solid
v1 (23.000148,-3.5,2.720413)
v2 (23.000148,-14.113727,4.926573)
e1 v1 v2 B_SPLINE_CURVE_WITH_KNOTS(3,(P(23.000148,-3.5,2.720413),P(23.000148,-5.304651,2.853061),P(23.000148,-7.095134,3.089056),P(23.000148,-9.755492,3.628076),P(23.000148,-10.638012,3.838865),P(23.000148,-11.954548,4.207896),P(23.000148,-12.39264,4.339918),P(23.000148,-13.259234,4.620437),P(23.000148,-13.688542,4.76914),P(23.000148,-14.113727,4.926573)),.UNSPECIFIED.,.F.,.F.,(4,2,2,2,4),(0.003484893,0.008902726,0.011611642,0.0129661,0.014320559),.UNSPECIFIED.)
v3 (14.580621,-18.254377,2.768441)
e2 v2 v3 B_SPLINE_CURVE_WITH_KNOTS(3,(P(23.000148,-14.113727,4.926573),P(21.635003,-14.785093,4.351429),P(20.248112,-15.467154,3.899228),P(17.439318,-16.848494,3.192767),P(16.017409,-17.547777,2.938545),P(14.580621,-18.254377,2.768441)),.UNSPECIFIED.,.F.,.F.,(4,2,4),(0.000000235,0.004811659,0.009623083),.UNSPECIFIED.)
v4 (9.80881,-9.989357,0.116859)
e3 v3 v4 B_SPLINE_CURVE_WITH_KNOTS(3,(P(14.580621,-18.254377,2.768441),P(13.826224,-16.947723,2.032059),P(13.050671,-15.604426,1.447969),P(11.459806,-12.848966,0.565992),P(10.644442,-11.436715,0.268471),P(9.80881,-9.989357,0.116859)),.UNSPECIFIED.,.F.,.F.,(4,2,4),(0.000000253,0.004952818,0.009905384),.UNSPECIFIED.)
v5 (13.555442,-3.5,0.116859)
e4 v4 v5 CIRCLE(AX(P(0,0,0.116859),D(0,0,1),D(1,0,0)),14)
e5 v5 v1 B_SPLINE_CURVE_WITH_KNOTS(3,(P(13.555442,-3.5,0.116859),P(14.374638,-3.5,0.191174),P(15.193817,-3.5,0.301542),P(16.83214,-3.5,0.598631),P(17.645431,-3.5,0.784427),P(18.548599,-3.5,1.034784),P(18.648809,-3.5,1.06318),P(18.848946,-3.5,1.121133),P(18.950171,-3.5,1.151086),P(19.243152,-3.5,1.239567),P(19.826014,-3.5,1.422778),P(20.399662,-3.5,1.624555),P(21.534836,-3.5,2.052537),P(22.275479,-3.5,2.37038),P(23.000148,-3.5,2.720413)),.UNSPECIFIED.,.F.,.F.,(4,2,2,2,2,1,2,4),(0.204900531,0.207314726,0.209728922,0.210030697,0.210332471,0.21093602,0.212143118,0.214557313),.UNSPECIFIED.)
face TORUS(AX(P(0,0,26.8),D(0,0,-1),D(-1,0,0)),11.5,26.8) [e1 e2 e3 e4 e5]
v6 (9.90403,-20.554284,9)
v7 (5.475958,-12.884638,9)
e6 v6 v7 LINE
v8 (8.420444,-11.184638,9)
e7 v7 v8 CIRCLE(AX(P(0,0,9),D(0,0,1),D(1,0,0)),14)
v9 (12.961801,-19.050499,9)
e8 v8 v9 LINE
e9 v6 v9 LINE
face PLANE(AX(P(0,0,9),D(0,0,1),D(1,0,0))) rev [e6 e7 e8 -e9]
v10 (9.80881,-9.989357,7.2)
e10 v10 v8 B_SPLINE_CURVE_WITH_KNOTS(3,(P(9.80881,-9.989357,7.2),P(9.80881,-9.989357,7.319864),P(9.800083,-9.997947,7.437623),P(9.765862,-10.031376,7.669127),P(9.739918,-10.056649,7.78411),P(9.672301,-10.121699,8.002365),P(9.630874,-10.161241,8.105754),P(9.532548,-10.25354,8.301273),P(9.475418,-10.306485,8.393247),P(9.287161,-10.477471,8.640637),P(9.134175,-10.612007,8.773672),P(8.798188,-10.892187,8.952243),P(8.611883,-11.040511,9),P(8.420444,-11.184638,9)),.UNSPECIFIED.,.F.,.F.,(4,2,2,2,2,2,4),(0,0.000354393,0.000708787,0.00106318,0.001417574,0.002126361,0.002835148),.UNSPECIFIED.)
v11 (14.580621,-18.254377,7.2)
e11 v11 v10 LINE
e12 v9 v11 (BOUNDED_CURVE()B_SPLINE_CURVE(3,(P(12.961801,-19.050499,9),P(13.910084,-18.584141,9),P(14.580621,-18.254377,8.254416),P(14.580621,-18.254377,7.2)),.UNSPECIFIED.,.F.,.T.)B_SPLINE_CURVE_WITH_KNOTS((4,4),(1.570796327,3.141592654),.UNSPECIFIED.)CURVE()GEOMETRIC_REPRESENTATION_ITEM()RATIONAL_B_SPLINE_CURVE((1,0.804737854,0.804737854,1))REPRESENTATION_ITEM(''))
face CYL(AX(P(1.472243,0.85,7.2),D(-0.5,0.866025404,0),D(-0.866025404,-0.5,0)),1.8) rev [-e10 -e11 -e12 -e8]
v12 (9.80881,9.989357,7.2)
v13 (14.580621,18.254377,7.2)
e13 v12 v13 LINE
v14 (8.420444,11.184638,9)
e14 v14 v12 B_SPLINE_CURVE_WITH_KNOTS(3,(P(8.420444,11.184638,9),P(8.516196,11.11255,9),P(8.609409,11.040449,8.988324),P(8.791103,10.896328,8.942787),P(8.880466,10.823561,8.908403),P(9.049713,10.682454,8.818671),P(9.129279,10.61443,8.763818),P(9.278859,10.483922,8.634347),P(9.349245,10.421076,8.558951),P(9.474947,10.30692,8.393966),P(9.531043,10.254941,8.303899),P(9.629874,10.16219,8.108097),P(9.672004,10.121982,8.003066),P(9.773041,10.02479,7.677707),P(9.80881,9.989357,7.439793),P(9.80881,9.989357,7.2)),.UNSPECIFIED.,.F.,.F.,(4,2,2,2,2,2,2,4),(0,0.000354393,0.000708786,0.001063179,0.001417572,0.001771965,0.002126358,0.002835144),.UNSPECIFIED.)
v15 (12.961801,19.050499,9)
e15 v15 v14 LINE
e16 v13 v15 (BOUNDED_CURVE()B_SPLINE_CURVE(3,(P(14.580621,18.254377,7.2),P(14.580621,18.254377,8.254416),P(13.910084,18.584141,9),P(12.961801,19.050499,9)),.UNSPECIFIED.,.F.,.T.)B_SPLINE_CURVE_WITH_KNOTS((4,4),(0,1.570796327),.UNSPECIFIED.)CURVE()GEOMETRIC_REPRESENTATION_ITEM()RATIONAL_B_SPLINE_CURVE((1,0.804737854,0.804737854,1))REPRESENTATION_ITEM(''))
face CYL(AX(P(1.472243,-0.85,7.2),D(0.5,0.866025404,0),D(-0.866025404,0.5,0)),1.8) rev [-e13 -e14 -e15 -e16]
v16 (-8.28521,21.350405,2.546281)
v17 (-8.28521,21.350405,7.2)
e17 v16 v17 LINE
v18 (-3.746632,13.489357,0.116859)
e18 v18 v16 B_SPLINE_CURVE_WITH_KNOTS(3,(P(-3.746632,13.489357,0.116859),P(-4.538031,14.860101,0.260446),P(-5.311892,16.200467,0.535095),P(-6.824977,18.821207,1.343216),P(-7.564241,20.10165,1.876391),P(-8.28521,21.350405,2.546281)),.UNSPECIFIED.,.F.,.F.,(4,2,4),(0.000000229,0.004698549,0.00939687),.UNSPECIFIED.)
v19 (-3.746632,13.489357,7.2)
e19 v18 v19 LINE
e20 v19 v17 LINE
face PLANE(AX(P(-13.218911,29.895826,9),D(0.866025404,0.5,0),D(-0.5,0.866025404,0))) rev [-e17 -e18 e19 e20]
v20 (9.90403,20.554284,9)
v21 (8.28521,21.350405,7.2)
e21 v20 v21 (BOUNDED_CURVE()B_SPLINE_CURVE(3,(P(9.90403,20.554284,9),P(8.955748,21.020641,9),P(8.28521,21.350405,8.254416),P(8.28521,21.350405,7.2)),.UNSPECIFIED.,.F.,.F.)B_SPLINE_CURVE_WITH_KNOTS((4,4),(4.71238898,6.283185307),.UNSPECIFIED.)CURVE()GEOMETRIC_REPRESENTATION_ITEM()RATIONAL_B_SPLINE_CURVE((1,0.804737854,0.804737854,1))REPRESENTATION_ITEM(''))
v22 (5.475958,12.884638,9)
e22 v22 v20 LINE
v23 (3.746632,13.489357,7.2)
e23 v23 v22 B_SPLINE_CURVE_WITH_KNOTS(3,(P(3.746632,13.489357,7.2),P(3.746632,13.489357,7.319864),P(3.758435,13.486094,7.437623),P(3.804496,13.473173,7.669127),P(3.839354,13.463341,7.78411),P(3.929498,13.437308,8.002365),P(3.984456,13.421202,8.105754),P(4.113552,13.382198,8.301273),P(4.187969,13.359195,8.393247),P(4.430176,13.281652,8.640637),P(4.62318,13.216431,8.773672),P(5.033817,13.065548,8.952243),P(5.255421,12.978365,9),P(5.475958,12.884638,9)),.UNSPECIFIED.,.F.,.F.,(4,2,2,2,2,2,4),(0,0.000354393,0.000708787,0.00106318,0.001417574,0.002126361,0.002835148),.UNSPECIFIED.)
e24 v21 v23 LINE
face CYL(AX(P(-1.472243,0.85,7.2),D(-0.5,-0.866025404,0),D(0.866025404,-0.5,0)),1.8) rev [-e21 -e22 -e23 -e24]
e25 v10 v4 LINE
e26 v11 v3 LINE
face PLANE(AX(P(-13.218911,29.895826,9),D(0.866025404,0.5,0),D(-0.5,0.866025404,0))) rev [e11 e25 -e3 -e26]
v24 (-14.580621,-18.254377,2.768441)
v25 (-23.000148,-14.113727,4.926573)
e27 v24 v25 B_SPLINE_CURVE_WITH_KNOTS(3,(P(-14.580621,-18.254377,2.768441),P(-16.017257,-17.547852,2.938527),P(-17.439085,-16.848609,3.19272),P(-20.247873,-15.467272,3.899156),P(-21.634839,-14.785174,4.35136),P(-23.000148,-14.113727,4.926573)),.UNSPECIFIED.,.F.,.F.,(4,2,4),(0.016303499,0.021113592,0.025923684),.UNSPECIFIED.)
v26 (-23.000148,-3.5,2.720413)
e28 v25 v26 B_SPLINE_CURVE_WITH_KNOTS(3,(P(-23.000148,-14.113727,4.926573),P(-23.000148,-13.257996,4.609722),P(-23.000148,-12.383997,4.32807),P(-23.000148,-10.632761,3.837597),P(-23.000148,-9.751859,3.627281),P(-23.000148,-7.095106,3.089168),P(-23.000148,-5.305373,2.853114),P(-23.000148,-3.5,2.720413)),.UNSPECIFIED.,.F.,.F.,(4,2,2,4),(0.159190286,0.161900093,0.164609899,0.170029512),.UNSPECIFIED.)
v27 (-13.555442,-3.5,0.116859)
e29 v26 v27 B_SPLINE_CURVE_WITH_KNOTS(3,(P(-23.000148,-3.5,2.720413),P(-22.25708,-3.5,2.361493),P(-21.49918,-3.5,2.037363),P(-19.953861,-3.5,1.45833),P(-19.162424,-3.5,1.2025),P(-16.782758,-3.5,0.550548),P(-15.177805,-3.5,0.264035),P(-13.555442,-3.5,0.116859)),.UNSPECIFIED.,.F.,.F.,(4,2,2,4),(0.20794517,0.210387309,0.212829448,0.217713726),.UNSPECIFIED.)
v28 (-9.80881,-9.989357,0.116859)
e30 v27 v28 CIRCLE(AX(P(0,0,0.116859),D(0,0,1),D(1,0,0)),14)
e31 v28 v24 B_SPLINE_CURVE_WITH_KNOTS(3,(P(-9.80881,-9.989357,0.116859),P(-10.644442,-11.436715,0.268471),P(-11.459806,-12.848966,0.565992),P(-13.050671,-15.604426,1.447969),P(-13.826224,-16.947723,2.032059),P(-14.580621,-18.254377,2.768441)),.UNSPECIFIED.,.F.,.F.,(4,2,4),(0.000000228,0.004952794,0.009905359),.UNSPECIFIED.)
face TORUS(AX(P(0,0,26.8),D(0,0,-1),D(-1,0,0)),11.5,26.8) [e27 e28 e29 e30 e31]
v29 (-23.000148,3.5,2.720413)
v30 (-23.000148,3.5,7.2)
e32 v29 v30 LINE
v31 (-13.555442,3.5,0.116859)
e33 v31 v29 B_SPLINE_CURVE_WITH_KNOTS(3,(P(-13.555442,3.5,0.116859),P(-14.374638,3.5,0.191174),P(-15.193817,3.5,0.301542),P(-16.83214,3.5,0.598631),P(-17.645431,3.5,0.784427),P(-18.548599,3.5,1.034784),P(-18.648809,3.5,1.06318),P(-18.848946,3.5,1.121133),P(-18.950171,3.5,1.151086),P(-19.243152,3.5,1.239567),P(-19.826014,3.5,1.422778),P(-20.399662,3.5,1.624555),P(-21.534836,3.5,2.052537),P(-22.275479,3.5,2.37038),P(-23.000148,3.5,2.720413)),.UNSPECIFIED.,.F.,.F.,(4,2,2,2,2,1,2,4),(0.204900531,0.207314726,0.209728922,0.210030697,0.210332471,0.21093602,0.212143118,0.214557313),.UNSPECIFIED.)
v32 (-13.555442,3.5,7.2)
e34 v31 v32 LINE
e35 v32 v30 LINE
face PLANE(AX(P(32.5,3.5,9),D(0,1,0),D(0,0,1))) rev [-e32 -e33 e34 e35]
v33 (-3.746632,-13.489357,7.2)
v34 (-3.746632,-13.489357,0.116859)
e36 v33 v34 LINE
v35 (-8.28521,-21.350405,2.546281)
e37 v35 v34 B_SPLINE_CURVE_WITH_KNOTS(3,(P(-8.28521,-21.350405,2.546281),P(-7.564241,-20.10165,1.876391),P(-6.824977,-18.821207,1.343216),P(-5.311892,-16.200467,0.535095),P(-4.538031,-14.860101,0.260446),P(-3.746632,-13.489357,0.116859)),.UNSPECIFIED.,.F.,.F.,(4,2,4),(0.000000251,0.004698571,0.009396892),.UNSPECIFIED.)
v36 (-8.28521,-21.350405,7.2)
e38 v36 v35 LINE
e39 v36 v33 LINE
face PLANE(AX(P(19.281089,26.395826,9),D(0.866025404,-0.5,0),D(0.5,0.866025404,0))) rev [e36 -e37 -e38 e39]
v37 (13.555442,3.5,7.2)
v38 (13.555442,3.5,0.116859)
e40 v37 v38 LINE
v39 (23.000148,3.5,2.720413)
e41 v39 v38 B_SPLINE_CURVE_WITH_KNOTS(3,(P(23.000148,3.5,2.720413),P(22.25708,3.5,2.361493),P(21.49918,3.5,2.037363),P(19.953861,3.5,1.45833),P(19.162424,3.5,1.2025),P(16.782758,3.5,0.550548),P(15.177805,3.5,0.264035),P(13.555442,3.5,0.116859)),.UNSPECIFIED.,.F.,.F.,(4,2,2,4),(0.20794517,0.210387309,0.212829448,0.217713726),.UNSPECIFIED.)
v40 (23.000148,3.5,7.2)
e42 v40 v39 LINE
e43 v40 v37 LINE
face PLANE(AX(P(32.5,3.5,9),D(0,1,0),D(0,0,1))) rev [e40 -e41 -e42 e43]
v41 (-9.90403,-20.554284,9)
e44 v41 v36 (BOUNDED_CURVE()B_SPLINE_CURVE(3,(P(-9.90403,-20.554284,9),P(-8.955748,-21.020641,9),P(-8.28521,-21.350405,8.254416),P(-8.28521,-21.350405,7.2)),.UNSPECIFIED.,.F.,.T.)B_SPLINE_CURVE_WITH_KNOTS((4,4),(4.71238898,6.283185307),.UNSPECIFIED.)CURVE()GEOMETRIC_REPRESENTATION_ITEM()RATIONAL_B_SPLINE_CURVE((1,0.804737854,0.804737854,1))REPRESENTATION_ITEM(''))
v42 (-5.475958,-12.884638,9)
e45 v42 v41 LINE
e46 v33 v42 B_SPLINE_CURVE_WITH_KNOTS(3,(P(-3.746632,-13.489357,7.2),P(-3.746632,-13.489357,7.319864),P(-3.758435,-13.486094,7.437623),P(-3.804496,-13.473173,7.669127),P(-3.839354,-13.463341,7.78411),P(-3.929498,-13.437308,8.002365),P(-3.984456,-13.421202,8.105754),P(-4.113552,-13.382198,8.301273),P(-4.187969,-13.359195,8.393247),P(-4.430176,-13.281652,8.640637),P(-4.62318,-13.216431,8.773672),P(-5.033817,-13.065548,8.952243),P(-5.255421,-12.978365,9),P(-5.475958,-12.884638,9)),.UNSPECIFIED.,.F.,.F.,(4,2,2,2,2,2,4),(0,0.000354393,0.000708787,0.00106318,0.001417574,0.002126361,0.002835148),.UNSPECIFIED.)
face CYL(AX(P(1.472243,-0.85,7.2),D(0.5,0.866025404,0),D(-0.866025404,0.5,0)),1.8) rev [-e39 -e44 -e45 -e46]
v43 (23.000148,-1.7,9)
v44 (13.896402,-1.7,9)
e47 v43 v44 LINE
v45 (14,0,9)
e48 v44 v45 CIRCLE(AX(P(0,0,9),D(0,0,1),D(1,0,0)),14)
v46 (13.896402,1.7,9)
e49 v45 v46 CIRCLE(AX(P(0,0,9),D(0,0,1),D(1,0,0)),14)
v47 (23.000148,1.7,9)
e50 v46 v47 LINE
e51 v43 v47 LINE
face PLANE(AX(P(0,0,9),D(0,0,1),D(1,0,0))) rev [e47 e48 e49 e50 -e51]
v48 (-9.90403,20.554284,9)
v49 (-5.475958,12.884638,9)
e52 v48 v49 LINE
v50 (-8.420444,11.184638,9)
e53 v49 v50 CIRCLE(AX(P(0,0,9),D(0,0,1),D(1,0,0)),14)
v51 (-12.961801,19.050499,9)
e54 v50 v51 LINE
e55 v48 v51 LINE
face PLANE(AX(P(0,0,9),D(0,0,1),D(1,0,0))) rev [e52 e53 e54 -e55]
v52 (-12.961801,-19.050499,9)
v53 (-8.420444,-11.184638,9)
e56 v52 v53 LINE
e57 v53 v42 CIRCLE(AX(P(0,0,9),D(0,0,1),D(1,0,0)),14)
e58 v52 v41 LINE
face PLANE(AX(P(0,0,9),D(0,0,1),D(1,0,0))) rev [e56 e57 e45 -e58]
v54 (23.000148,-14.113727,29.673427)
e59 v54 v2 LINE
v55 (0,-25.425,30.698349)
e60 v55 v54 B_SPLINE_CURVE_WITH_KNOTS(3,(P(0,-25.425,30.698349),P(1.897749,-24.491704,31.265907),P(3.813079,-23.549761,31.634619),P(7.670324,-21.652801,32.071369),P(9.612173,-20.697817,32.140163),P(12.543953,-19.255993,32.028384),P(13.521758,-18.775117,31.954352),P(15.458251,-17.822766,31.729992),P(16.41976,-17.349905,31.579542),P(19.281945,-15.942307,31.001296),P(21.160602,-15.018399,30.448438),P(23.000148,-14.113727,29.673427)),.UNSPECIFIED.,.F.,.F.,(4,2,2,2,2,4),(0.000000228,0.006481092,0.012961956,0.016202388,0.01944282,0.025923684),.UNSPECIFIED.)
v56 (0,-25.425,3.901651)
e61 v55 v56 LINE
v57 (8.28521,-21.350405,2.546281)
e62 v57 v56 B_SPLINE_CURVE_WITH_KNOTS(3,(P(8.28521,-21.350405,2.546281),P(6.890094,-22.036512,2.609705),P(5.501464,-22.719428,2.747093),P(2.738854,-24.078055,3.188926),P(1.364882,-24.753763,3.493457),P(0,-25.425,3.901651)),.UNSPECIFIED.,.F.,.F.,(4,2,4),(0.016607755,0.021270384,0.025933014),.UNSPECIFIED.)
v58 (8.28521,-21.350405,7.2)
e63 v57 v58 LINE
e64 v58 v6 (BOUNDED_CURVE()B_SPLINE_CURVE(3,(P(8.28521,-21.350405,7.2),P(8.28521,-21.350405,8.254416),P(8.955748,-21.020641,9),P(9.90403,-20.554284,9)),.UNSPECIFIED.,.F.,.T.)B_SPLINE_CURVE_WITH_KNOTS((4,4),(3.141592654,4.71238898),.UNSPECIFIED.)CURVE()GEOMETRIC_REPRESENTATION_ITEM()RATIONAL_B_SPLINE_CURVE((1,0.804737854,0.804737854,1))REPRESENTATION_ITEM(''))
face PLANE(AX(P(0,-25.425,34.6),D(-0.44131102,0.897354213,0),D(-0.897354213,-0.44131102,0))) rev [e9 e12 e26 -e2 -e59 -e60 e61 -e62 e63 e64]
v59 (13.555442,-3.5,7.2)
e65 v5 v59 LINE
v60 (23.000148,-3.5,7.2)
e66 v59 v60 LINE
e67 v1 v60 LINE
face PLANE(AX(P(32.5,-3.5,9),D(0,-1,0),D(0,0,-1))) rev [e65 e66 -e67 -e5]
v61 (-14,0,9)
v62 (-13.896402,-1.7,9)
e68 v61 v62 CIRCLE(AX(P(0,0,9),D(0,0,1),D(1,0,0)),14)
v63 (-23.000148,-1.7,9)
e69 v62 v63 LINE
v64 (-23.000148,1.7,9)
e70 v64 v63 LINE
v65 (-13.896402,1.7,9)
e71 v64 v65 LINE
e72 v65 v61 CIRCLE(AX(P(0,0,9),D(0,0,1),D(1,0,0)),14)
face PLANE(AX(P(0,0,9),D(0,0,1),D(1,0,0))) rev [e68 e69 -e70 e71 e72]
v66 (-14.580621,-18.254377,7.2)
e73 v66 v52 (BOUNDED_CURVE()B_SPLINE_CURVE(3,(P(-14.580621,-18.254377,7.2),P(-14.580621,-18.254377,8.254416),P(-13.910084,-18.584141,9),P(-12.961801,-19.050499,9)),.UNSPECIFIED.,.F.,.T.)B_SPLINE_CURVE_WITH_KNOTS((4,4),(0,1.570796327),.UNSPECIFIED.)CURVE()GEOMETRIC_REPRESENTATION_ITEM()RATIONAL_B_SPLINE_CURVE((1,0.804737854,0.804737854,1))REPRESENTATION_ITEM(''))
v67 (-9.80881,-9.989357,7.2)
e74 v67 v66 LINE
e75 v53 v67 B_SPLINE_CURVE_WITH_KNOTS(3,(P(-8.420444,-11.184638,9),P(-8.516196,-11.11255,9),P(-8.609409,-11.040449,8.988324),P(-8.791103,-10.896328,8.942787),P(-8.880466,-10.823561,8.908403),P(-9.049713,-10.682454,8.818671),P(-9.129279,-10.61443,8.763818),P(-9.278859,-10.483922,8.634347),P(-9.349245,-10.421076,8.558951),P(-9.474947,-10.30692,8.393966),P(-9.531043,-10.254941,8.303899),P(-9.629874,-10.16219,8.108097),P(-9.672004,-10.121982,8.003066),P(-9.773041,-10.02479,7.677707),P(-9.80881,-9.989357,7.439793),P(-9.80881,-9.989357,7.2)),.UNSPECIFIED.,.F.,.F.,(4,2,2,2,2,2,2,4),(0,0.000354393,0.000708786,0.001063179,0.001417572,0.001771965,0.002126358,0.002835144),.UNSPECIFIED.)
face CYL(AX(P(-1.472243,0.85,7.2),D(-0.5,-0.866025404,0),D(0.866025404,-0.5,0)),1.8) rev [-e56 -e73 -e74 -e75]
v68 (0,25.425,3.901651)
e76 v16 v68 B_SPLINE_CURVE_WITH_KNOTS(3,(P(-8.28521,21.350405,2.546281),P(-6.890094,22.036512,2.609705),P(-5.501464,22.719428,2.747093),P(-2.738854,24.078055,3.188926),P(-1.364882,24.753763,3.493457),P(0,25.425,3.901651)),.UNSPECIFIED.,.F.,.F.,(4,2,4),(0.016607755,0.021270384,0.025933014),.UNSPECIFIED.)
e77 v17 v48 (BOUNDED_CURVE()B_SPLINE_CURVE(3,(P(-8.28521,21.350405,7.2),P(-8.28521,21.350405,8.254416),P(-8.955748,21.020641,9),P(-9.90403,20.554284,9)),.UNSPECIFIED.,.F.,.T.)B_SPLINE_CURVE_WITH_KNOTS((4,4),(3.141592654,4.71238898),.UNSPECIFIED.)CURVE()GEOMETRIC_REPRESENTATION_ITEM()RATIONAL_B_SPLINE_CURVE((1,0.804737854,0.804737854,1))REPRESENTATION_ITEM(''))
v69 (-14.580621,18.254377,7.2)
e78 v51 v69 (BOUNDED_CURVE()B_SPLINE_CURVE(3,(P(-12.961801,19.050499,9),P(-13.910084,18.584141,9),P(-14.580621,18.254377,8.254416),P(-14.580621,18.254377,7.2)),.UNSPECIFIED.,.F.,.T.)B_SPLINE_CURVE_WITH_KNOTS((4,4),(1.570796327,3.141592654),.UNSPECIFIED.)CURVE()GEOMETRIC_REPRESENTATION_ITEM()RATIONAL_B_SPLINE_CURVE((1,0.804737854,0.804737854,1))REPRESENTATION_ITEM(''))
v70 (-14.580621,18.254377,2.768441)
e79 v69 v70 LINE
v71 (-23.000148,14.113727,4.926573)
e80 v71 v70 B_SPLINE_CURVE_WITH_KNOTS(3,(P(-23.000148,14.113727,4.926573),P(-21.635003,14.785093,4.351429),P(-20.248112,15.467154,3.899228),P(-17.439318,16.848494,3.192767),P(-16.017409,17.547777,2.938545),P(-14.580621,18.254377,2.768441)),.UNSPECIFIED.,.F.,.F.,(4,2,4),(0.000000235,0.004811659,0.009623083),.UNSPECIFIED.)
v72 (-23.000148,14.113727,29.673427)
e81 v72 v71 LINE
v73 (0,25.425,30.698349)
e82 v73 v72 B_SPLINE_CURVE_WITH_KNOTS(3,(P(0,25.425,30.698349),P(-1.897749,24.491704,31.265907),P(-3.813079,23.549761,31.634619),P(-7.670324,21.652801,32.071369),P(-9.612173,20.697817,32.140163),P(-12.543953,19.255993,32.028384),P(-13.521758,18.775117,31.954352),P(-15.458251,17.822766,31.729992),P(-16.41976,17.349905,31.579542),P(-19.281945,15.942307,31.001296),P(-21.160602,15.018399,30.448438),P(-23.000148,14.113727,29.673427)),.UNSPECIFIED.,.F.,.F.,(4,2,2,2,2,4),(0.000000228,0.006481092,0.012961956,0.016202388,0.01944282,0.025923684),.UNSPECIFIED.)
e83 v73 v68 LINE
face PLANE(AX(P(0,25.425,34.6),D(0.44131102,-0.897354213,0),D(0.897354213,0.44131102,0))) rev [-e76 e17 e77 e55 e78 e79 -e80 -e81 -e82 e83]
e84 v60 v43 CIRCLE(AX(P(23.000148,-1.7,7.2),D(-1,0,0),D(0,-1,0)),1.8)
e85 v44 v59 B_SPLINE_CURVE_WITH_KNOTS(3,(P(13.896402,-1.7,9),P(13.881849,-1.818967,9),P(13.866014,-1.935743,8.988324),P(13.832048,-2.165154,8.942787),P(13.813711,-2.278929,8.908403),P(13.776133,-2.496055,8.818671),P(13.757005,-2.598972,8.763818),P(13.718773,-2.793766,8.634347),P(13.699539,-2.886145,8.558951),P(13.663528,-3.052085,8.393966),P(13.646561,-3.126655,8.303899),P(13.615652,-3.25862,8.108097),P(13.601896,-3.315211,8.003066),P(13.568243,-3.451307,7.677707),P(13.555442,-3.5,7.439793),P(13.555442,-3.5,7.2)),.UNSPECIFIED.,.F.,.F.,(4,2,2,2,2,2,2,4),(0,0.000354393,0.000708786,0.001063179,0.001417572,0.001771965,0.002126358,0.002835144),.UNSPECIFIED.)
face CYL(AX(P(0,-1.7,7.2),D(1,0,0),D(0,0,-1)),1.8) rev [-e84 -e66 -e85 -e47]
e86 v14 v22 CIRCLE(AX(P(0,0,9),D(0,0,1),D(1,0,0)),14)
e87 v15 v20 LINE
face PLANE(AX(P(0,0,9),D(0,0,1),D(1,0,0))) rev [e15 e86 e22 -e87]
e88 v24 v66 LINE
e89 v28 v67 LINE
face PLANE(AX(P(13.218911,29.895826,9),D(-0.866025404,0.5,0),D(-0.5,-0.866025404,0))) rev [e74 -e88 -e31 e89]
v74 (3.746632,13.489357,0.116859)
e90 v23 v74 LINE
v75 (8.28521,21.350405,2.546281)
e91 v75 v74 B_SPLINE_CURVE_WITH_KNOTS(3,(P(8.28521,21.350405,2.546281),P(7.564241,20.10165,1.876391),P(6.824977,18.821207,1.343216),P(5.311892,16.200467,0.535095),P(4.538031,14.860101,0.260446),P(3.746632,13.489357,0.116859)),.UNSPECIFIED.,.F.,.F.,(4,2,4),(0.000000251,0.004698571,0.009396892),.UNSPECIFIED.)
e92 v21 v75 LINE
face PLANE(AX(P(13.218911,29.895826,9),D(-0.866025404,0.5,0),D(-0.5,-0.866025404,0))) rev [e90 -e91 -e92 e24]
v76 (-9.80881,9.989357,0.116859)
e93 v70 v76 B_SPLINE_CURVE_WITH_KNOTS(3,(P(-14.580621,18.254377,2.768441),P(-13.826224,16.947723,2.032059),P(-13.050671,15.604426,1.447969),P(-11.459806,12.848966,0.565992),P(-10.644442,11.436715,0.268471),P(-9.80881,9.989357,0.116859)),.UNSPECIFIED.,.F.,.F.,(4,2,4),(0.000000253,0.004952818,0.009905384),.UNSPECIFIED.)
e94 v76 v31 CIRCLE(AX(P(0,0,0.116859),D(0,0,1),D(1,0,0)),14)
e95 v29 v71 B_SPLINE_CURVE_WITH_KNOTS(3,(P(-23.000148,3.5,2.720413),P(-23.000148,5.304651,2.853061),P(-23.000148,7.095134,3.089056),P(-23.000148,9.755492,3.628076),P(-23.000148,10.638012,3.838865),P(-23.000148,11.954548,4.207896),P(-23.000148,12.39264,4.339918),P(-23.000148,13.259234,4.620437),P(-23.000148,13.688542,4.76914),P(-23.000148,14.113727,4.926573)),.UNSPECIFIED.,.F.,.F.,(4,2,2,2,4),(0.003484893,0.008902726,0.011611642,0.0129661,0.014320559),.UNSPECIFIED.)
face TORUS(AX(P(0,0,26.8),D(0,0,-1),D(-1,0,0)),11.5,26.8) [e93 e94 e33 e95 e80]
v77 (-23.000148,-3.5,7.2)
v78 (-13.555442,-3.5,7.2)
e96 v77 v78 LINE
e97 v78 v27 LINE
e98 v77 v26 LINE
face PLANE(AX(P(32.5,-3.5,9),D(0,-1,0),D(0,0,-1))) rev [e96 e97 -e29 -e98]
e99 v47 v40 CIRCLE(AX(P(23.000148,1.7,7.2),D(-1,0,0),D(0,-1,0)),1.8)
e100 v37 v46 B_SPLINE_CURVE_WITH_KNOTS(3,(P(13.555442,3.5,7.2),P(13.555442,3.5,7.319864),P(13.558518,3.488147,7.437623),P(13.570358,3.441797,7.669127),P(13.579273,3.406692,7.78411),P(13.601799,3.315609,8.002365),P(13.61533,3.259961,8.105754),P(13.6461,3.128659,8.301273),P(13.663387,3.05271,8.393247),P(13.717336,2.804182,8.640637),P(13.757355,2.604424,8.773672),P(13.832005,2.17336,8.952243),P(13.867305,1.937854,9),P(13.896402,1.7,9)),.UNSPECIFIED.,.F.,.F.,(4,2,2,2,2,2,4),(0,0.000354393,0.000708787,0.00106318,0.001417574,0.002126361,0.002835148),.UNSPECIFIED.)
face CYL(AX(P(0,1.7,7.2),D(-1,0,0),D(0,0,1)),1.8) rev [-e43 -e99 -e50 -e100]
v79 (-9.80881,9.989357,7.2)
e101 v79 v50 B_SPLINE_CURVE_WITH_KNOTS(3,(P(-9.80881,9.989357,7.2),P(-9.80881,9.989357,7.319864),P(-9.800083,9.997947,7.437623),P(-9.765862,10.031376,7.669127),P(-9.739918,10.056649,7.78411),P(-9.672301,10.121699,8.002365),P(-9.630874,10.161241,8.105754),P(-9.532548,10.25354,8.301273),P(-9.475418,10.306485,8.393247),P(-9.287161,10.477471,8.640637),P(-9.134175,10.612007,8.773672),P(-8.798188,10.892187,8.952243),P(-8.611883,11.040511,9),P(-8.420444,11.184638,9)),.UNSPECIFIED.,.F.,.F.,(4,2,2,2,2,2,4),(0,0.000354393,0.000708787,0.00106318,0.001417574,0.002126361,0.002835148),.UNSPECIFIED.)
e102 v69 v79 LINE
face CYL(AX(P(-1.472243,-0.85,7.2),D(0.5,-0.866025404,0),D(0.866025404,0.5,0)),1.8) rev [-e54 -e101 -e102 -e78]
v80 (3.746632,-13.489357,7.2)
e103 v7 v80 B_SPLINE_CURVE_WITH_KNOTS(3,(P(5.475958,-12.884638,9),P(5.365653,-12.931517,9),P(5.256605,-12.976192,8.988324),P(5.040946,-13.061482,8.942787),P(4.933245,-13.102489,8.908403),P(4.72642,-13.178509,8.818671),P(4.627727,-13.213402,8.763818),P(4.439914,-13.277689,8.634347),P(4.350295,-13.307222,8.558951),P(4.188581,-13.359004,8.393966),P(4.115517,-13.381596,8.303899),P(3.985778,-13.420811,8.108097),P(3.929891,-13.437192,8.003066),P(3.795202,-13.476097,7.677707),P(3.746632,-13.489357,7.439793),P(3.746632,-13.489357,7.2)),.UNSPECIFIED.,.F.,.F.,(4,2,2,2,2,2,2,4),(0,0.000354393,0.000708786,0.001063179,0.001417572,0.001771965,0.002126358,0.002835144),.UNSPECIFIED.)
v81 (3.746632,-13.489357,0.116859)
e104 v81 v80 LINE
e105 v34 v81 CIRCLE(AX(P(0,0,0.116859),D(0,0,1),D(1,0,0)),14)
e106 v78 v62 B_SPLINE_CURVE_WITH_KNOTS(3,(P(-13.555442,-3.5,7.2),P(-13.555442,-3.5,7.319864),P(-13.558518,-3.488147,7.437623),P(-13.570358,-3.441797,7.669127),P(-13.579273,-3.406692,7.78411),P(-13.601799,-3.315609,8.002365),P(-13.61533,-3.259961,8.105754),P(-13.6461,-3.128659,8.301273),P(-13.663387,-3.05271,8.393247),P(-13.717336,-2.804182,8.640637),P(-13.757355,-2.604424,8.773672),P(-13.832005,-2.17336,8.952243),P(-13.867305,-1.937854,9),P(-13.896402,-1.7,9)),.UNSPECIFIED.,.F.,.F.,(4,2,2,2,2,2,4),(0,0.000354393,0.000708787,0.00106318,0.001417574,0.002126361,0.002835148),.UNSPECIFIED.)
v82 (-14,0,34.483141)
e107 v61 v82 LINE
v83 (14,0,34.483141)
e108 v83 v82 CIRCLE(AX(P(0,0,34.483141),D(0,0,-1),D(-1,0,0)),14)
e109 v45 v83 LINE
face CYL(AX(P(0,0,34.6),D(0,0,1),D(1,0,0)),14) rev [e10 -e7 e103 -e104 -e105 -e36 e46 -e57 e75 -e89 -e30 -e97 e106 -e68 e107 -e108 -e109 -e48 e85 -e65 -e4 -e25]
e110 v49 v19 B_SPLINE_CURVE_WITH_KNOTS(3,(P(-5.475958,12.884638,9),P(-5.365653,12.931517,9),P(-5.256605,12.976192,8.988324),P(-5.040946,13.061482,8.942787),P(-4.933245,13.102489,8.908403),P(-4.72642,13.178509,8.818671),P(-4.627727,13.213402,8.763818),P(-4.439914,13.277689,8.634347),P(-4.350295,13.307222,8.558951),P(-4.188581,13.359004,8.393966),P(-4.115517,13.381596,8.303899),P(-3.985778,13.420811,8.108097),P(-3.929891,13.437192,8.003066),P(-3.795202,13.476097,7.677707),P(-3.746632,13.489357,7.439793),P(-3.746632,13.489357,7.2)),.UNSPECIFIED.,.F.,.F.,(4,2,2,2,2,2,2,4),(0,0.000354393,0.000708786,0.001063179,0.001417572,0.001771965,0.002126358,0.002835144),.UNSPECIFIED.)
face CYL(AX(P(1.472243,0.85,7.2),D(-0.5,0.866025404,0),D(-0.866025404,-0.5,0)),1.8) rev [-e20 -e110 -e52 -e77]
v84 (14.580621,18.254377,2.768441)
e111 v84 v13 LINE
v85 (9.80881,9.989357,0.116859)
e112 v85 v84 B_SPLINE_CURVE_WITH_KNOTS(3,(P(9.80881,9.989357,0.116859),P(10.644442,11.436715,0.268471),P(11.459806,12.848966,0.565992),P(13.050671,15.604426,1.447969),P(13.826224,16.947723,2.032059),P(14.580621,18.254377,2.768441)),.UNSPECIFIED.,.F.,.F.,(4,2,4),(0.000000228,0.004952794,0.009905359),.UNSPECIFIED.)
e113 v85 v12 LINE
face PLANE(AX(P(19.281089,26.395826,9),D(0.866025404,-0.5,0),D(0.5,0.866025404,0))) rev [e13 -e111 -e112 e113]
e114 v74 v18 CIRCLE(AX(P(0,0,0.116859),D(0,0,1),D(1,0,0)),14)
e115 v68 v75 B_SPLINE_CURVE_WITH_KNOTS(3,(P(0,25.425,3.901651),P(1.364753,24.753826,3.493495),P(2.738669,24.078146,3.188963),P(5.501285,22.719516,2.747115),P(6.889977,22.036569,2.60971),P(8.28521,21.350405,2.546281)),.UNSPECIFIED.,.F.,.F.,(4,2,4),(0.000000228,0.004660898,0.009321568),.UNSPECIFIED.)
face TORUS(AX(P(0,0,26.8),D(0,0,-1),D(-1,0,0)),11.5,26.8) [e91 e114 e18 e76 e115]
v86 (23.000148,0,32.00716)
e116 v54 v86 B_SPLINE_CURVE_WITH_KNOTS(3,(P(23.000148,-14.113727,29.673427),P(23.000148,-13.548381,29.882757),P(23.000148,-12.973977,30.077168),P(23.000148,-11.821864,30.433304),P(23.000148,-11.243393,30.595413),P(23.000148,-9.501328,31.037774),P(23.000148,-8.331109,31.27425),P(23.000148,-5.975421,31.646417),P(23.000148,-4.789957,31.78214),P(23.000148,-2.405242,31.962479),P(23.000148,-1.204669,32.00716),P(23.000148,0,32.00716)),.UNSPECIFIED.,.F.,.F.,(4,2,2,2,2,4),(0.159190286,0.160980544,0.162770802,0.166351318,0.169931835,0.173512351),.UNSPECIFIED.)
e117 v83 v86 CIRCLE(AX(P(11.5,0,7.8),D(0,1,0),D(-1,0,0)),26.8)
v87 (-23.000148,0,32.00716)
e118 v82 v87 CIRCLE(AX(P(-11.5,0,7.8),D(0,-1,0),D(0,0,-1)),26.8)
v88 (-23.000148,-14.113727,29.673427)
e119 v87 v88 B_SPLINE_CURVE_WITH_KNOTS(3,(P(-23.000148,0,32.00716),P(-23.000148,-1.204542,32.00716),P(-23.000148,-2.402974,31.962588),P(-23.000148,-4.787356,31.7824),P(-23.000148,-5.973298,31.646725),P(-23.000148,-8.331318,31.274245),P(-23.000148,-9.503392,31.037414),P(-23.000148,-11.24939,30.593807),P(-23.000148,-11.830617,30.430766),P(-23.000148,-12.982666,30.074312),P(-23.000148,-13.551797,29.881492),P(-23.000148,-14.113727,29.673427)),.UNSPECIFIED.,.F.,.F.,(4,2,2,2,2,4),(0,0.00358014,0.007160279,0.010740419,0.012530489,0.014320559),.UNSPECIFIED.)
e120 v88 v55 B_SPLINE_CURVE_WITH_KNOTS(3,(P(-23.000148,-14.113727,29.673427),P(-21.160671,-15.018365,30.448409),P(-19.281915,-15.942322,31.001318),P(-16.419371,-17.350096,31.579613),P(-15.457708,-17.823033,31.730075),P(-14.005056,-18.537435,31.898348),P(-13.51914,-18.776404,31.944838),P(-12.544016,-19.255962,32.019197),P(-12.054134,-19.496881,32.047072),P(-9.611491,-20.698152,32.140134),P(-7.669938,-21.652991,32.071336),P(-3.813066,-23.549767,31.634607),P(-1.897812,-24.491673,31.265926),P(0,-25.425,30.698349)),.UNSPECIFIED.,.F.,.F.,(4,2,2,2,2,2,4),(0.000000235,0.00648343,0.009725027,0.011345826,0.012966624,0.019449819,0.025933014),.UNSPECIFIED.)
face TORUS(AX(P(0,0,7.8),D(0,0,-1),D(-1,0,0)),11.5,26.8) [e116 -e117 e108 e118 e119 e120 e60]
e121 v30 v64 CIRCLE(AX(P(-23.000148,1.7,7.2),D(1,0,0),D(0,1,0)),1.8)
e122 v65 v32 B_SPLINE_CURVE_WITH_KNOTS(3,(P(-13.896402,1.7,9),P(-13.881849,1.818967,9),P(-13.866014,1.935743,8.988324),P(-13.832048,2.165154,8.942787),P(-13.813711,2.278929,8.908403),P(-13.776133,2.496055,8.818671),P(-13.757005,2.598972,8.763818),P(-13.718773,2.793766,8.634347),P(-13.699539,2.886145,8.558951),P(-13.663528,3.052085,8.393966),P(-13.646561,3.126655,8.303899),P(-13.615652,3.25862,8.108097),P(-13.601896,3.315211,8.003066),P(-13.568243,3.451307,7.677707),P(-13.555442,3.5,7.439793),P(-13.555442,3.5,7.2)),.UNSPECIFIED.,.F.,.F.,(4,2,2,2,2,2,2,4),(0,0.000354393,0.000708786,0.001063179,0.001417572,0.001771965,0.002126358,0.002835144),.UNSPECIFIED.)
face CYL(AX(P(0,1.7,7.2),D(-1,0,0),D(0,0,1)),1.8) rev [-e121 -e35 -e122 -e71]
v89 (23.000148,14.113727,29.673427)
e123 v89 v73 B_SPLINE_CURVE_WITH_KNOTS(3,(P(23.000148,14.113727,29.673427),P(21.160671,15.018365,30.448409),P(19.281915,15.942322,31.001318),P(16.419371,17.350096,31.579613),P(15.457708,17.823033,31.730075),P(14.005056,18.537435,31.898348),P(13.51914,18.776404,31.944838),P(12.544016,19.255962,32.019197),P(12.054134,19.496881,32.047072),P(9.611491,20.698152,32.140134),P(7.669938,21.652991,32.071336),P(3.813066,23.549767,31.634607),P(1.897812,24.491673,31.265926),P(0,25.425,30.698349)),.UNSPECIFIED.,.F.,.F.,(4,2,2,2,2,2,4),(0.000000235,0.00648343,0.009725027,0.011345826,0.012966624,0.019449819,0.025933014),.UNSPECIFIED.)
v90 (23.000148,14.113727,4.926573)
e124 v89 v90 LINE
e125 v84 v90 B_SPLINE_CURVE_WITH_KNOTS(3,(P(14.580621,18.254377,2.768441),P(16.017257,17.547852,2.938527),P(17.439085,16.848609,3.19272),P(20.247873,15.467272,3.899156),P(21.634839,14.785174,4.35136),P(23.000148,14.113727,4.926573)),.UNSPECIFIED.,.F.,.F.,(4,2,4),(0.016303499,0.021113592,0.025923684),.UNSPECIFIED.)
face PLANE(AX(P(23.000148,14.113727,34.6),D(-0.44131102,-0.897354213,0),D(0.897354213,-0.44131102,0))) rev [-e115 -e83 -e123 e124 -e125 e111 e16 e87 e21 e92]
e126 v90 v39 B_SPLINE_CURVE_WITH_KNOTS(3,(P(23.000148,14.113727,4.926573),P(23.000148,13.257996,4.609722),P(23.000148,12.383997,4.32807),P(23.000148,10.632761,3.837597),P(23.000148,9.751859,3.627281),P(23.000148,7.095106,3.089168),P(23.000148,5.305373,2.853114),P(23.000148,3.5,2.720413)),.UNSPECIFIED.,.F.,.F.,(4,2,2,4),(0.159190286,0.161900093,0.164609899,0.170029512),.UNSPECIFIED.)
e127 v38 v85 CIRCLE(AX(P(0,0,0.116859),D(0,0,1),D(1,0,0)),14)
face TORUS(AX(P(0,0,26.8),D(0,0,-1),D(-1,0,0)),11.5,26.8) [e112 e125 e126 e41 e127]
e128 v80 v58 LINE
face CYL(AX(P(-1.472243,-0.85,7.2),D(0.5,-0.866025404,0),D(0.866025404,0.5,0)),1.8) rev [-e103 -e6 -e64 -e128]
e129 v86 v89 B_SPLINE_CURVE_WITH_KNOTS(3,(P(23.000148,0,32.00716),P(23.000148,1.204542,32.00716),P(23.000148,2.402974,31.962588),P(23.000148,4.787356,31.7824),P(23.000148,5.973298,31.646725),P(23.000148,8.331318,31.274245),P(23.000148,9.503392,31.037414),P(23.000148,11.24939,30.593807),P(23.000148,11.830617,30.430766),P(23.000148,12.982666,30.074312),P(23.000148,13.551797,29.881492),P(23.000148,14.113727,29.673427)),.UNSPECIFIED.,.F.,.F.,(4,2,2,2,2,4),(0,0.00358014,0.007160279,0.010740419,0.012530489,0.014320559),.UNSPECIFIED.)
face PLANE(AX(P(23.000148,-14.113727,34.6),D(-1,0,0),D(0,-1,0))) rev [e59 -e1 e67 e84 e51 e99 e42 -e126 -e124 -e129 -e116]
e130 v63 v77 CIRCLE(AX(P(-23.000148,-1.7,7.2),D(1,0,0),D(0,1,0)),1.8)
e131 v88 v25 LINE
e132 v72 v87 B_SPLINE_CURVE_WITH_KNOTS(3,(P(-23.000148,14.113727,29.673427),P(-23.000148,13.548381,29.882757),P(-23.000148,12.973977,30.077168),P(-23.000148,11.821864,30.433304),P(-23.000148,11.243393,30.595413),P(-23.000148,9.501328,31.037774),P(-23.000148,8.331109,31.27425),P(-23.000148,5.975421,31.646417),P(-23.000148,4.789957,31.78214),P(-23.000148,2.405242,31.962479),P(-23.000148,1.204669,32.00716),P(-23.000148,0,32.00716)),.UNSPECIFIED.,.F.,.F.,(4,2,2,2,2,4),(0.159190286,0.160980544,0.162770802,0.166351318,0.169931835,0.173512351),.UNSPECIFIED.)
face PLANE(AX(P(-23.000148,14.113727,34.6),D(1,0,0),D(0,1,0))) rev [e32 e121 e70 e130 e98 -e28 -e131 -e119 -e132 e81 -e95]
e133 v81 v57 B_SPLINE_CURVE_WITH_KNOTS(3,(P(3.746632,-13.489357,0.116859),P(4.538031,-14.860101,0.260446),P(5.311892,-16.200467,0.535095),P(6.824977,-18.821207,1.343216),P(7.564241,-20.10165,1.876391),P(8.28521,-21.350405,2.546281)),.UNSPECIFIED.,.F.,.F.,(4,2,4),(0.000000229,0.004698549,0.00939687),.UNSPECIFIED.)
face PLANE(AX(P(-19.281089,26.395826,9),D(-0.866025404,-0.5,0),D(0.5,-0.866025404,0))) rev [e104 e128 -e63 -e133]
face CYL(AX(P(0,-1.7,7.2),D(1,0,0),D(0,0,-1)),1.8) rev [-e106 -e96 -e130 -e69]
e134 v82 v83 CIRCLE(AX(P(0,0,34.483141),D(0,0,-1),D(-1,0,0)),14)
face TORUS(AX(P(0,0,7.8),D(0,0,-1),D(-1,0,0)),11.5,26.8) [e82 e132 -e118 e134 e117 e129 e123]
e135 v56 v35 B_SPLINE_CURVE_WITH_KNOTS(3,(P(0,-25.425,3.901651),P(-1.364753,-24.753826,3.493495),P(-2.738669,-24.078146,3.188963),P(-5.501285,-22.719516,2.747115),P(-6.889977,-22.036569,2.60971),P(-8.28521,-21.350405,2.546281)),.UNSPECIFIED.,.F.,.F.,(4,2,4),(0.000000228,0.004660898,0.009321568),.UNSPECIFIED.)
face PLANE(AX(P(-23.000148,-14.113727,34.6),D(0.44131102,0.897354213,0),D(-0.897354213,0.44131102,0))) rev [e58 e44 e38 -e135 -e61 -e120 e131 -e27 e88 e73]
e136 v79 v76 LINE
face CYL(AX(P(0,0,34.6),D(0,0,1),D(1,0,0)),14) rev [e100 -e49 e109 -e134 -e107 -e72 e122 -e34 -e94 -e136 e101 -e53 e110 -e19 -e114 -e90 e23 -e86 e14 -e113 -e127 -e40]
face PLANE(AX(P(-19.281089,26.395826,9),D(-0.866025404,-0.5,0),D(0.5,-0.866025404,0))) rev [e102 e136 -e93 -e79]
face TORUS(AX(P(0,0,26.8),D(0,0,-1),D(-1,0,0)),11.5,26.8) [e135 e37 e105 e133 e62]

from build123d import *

# Parameters (mm, degrees)
EXTRUDE_1_DEPTH          = 34.6
SKETCH_3_W               = 65
SKETCH_3_H               = 7
CUT_EXTRUDE_1_DEPTH      = 9
PATTERN_CIRCULAR_1_COUNT = 3
PATTERN_CIRCULAR_1_ANGLE = 120
M30X2_0_1_D              = 28
FILLET_2_R               = 1.8


with BuildPart() as part:
    # 草图1 → 凸台-拉伸1 (new body)
    with BuildSketch(Plane.XY):
        Polygon((0, 25.425), (-23.00014754, 14.1137269), (-23.00014754, -14.1137269), (0, -25.425), (23.00014754, -14.1137269), (23.00014754, 14.1137269), align=None)
    extrude(amount=EXTRUDE_1_DEPTH)

    # 草图3 → 切除-拉伸1 (cut)
    with BuildSketch(Plane(origin=(0, 0, 0), x_dir=(-1, 0, 0), z_dir=(0, 0, -1))):
        Rectangle(SKETCH_3_W, SKETCH_3_H)
    cut_extrude_1 = extrude(amount=-CUT_EXTRUDE_1_DEPTH, mode=Mode.SUBTRACT)

    # 阵列(圆周)1: 切除-拉伸1 ×3 about axis
    pattern_circular_1_axis = Axis((0, 0, 0), (0, 0, 1))
    for i in range(1, PATTERN_CIRCULAR_1_COUNT):
        add(cut_extrude_1.rotate(pattern_circular_1_axis, i * PATTERN_CIRCULAR_1_ANGLE / (PATTERN_CIRCULAR_1_COUNT - 1)), mode=Mode.SUBTRACT)

    # M30x2.0 螺纹孔1 (through all)
    with Locations(Plane.XY.offset(34.6)):
        with Locations((0, 0)):
            Hole(M30X2_0_1_D / 2)

    # 圆角2
    fillet_2_edges = [part.edges().sort_by_distance(p)[0] for p in [
        (-12.194715533, 14.121866887, 9),
        (6.015921174, 17.419881127, 9),
        (-6.015921174, -17.419881127, 9),
        (12.194715533, -14.121866887, 9),
        (-18.277794626, -3.5, 9),
        (18.277794626, 3.5, 9),
        (-18.277794626, 3.5, 9),
        (18.277794626, -3.5, 9),
        (-6.015921174, 17.419881127, 9),
        (6.015921174, -17.419881127, 9),
        (12.194715533, 14.121866887, 9),
        (-12.194715533, -14.121866887, 9),
    ]]
    fillet(fillet_2_edges, radius=FILLET_2_R)

    # 草图8 → 切除-旋转1 (revolve, cut)
    with BuildSketch(Plane(origin=(0, 0, 0), x_dir=(1, 0, 0), z_dir=(0, 1, 0)), mode=Mode.PRIVATE) as cut_revolve_1_sk:
        with BuildLine():
            Line((11.5, 0), (33.520524336, 0))
            Line((33.520524336, 0), (33.520524336, -11.524643769))
            ThreePointArc((33.520524336, -11.524643769), (23.926995876, -3.055321154), (11.5, 0))
        make_face()
        with BuildLine():
            Line((11.5, -34.6), (33.520524336, -34.6))
            Line((33.520524336, -34.6), (33.520524336, -23.075356231))
            ThreePointArc((33.520524336, -23.075356231), (23.926995876, -31.544678846), (11.5, -34.6))
        make_face()
    revolve(cut_revolve_1_sk.sketch.rotate(Axis((0, 0, -1.73), (0, 0, 1)), 353.025443337), axis=Axis((0, 0, -1.73), (0, 0, 1)), mode=Mode.SUBTRACT)


solid = part.part
